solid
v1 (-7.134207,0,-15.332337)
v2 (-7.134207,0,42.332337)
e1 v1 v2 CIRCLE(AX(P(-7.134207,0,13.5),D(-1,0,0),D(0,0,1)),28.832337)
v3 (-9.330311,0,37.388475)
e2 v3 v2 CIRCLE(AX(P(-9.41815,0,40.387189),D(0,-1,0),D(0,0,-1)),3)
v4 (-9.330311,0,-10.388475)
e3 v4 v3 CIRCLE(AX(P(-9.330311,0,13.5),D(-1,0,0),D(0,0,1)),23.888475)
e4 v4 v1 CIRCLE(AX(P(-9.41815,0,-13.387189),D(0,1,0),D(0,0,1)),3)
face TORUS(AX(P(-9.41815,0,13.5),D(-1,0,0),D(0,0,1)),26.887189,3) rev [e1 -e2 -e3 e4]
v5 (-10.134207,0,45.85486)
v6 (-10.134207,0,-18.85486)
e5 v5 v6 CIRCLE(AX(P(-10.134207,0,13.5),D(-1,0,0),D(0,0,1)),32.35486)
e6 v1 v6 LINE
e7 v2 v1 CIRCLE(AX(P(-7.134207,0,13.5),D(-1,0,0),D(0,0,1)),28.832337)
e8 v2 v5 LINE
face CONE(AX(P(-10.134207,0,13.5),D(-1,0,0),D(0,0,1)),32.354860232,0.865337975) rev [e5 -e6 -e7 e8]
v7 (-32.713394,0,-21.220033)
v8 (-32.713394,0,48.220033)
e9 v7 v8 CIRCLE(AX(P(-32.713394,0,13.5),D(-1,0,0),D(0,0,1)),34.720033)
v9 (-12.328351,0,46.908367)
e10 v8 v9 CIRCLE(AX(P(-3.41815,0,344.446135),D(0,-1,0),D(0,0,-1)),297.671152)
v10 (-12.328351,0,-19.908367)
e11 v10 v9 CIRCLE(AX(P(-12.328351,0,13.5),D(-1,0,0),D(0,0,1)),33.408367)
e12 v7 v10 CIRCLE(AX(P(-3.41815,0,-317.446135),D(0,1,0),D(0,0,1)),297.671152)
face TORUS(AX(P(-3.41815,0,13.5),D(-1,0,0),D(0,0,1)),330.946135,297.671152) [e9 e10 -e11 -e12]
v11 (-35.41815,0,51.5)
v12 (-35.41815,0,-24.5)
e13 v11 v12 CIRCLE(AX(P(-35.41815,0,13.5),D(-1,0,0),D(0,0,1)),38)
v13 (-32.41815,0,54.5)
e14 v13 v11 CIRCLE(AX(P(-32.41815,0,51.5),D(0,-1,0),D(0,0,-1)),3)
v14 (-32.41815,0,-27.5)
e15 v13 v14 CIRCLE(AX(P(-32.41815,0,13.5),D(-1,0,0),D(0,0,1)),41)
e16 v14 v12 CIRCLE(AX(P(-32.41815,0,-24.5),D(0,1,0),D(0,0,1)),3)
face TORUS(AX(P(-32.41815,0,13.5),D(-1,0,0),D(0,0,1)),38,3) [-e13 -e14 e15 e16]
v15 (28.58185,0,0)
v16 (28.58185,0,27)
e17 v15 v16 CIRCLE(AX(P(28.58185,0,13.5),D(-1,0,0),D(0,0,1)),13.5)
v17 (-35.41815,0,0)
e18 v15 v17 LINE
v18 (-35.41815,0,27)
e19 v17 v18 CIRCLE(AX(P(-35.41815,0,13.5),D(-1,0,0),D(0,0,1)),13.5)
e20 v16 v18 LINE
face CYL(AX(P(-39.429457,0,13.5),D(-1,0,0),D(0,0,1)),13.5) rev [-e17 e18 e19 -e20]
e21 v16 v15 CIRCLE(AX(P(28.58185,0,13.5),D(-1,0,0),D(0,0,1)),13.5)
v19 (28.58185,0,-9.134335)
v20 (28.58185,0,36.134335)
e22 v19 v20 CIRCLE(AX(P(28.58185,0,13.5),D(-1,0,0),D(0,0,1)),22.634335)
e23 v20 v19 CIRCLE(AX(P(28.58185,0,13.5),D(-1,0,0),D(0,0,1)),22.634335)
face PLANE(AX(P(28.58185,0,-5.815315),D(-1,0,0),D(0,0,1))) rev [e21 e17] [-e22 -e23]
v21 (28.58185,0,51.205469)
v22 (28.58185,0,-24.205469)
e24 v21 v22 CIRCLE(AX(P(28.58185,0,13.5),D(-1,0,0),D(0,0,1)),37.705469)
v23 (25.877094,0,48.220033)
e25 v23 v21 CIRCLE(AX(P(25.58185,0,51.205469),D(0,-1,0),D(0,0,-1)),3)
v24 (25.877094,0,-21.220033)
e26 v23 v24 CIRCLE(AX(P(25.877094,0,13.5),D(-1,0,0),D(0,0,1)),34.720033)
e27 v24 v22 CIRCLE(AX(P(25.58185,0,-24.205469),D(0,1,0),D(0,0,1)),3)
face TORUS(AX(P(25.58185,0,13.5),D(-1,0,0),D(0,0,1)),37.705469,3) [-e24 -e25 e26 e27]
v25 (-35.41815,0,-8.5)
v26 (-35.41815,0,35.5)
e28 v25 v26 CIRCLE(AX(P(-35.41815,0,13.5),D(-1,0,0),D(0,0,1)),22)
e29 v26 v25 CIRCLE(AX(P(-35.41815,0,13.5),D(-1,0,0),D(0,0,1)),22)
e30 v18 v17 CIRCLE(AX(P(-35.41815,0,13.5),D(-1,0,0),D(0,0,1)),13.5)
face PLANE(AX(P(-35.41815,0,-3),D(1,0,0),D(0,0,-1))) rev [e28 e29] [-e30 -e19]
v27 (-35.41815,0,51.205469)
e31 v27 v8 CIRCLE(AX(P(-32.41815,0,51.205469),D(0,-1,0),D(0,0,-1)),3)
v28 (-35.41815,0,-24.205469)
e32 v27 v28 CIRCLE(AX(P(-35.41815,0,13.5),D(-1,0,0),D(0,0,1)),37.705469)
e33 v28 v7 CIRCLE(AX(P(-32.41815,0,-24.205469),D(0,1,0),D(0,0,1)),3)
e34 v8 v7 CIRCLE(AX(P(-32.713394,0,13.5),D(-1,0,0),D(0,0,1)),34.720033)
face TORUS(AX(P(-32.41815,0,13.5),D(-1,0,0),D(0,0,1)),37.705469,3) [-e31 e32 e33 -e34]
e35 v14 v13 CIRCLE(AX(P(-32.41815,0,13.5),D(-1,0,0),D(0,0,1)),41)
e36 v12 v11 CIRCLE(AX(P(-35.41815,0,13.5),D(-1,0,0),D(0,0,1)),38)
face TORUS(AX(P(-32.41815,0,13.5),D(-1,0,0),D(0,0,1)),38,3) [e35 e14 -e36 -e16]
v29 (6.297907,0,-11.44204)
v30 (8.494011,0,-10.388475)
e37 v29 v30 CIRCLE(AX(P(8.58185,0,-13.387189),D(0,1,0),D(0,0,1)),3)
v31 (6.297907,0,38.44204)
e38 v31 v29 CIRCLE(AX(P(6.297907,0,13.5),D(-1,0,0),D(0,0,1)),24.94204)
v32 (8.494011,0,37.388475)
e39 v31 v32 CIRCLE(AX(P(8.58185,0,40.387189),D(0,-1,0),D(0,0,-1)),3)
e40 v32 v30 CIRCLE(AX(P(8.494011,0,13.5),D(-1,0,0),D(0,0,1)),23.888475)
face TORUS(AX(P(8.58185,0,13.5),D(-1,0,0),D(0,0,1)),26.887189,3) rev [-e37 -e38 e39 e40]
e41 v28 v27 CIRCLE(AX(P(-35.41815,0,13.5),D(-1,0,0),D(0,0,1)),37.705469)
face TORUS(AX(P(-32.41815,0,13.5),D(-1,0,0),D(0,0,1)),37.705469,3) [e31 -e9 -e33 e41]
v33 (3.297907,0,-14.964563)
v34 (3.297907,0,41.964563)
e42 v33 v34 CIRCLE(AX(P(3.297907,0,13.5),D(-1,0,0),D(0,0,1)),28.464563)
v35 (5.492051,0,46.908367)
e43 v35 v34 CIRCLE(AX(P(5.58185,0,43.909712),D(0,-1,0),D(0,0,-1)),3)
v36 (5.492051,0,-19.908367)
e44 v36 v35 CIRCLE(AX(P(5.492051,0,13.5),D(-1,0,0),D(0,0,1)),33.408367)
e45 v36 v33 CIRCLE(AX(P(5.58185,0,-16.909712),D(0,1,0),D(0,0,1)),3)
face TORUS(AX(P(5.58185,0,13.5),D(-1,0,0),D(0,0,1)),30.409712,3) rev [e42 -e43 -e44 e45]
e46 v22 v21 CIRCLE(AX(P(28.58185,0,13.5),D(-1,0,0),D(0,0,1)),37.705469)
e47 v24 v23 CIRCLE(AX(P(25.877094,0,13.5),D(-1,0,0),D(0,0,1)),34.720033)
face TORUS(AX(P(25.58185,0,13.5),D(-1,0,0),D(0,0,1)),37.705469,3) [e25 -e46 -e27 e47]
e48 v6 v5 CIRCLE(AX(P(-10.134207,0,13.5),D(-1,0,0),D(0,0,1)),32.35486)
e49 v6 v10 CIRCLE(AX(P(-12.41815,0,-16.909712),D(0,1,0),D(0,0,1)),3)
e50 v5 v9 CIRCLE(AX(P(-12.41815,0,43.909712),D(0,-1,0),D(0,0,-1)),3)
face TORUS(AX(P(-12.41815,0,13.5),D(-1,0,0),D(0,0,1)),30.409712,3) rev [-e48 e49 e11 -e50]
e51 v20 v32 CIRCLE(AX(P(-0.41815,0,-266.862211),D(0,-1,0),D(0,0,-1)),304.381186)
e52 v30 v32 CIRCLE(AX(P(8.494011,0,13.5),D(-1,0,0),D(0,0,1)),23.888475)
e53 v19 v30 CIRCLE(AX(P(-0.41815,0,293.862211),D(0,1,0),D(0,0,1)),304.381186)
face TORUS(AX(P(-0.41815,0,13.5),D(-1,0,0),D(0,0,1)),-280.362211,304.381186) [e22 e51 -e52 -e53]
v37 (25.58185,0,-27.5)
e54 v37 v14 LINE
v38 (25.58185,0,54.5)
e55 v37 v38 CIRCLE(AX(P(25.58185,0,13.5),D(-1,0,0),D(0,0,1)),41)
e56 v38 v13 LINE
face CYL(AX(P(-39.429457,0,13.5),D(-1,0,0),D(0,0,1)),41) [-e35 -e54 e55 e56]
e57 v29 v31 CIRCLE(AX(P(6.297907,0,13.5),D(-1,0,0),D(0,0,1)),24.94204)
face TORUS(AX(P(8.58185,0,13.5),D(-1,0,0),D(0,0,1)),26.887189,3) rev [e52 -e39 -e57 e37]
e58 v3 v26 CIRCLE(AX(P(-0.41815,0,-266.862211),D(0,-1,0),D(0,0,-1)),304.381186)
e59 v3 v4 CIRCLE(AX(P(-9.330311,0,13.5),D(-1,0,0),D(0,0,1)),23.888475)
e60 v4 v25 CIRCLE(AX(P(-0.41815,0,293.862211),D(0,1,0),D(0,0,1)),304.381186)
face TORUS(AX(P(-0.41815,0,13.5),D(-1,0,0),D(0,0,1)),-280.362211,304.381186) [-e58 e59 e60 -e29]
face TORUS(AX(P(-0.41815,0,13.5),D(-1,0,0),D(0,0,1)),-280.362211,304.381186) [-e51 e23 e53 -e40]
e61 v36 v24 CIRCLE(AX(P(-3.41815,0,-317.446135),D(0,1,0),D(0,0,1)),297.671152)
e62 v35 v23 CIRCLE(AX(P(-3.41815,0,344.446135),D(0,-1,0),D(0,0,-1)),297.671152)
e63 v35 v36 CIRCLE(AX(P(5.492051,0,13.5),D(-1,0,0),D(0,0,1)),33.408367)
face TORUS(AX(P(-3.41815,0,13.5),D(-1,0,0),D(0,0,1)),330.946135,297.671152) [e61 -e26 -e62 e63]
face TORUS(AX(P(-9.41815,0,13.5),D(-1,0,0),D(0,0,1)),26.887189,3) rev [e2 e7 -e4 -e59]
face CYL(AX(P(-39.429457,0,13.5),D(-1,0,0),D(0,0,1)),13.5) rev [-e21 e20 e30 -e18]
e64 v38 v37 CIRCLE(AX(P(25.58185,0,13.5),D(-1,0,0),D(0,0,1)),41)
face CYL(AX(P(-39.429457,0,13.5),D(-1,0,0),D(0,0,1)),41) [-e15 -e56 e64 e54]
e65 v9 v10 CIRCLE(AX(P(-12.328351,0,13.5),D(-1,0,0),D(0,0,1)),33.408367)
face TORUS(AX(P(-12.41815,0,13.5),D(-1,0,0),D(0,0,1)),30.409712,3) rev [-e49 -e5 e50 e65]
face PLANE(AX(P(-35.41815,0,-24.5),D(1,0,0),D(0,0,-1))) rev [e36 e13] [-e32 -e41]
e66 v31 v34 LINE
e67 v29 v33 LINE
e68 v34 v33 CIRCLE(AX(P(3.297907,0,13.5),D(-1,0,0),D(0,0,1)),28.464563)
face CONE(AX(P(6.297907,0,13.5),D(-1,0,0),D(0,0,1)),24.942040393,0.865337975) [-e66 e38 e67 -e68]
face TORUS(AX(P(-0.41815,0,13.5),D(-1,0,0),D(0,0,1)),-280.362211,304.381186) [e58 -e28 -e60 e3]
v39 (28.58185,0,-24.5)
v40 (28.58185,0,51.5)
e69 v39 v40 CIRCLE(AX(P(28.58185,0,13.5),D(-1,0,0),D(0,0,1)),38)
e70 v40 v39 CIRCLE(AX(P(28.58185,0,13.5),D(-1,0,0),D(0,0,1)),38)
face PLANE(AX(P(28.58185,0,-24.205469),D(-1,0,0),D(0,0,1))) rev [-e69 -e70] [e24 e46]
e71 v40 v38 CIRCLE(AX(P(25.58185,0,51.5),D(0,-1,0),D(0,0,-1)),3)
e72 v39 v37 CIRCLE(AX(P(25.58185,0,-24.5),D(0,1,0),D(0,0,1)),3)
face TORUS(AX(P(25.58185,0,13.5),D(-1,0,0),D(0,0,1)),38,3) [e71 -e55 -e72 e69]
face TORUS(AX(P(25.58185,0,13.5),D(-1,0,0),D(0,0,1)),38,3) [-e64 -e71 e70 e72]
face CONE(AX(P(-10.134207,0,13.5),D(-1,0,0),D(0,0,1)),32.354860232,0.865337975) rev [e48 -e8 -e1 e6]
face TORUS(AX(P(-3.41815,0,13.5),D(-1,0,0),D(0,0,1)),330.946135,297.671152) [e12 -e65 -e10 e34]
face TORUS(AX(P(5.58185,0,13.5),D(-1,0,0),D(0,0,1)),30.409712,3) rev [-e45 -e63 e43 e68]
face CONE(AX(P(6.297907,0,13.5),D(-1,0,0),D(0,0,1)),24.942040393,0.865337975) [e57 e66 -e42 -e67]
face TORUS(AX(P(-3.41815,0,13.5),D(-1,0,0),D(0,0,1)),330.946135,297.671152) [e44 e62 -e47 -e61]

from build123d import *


with BuildPart() as part:
    # Sketch1 → Revolve1 (revolve)
    with BuildSketch(Plane(origin=(0, 0, 0), x_dir=(1, 0, 0), z_dir=(0, 1, 0)), mode=Mode.PRIVATE) as revolve1_sk:
        with BuildLine():
            Line((-35.418150087, 0), (28.581849913, 0))
            Line((28.581849913, 0), (28.581849913, 3))
            Line((28.581849913, 3), (28.581849913, 5.815314888))
            Line((28.581849913, 5.815314888), (28.581849913, 9.134334593))
            ThreePointArc((28.581849913, 9.134334593), (18.548299462, 9.927486707), (8.494011095, 10.388475153))
            ThreePointArc((8.494011095, 10.388475153), (7.284222242, 10.68234838), (6.297906579, 11.442040393))
            Line((6.297906579, 11.442040393), (3.297906579, 14.964563149))
            ThreePointArc((3.297906579, 14.964563149), (2.839777078, 18.126690149), (5.492050809, 19.90836741))
            ThreePointArc((5.492050809, 19.90836741), (15.695827227, 20.389287421), (25.877094288, 21.220033046))
            ThreePointArc((25.877094288, 21.220033046), (27.80510576, 22.191236773), (28.581849913, 24.20546949))
            Line((28.581849913, 24.20546949), (28.581849913, 24.5))
            ThreePointArc((28.581849913, 24.5), (27.703170256, 26.621320344), (25.581849913, 27.5))
            Line((25.581849913, 27.5), (-32.418150087, 27.5))
            ThreePointArc((-32.418150087, 27.5), (-34.539470431, 26.621320344), (-35.418150087, 24.5))
            Line((-35.418150087, 24.5), (-35.418150087, 24.20546949))
            ThreePointArc((-35.418150087, 24.20546949), (-34.641405934, 22.191236773), (-32.713394462, 21.220033046))
            ThreePointArc((-32.713394462, 21.220033046), (-22.532127402, 20.389287421), (-12.328350983, 19.90836741))
            ThreePointArc((-12.328350983, 19.90836741), (-11.119638388, 19.614127962), (-10.134206753, 18.854860232))
            Line((-10.134206753, 18.854860232), (-7.134206753, 15.332337476))
            ThreePointArc((-7.134206753, 15.332337476), (-6.676475178, 12.169314273), (-9.330311269, 10.388475153))
            ThreePointArc((-9.330311269, 10.388475153), (-22.394525119, 9.724589737), (-35.418150087, 8.5))
            Line((-35.418150087, 8.5), (-35.418150087, 5.815314888))
            Line((-35.418150087, 5.815314888), (-35.418150087, 3))
            Line((-35.418150087, 3), (-35.418150087, 0))
        make_face()
    revolve(revolve1_sk.sketch.rotate(Axis((-39.429457427, 0, 13.5), (1, 0, 0)), 180), axis=Axis((-39.429457427, 0, 13.5), (1, 0, 0)))


solid = part.part
